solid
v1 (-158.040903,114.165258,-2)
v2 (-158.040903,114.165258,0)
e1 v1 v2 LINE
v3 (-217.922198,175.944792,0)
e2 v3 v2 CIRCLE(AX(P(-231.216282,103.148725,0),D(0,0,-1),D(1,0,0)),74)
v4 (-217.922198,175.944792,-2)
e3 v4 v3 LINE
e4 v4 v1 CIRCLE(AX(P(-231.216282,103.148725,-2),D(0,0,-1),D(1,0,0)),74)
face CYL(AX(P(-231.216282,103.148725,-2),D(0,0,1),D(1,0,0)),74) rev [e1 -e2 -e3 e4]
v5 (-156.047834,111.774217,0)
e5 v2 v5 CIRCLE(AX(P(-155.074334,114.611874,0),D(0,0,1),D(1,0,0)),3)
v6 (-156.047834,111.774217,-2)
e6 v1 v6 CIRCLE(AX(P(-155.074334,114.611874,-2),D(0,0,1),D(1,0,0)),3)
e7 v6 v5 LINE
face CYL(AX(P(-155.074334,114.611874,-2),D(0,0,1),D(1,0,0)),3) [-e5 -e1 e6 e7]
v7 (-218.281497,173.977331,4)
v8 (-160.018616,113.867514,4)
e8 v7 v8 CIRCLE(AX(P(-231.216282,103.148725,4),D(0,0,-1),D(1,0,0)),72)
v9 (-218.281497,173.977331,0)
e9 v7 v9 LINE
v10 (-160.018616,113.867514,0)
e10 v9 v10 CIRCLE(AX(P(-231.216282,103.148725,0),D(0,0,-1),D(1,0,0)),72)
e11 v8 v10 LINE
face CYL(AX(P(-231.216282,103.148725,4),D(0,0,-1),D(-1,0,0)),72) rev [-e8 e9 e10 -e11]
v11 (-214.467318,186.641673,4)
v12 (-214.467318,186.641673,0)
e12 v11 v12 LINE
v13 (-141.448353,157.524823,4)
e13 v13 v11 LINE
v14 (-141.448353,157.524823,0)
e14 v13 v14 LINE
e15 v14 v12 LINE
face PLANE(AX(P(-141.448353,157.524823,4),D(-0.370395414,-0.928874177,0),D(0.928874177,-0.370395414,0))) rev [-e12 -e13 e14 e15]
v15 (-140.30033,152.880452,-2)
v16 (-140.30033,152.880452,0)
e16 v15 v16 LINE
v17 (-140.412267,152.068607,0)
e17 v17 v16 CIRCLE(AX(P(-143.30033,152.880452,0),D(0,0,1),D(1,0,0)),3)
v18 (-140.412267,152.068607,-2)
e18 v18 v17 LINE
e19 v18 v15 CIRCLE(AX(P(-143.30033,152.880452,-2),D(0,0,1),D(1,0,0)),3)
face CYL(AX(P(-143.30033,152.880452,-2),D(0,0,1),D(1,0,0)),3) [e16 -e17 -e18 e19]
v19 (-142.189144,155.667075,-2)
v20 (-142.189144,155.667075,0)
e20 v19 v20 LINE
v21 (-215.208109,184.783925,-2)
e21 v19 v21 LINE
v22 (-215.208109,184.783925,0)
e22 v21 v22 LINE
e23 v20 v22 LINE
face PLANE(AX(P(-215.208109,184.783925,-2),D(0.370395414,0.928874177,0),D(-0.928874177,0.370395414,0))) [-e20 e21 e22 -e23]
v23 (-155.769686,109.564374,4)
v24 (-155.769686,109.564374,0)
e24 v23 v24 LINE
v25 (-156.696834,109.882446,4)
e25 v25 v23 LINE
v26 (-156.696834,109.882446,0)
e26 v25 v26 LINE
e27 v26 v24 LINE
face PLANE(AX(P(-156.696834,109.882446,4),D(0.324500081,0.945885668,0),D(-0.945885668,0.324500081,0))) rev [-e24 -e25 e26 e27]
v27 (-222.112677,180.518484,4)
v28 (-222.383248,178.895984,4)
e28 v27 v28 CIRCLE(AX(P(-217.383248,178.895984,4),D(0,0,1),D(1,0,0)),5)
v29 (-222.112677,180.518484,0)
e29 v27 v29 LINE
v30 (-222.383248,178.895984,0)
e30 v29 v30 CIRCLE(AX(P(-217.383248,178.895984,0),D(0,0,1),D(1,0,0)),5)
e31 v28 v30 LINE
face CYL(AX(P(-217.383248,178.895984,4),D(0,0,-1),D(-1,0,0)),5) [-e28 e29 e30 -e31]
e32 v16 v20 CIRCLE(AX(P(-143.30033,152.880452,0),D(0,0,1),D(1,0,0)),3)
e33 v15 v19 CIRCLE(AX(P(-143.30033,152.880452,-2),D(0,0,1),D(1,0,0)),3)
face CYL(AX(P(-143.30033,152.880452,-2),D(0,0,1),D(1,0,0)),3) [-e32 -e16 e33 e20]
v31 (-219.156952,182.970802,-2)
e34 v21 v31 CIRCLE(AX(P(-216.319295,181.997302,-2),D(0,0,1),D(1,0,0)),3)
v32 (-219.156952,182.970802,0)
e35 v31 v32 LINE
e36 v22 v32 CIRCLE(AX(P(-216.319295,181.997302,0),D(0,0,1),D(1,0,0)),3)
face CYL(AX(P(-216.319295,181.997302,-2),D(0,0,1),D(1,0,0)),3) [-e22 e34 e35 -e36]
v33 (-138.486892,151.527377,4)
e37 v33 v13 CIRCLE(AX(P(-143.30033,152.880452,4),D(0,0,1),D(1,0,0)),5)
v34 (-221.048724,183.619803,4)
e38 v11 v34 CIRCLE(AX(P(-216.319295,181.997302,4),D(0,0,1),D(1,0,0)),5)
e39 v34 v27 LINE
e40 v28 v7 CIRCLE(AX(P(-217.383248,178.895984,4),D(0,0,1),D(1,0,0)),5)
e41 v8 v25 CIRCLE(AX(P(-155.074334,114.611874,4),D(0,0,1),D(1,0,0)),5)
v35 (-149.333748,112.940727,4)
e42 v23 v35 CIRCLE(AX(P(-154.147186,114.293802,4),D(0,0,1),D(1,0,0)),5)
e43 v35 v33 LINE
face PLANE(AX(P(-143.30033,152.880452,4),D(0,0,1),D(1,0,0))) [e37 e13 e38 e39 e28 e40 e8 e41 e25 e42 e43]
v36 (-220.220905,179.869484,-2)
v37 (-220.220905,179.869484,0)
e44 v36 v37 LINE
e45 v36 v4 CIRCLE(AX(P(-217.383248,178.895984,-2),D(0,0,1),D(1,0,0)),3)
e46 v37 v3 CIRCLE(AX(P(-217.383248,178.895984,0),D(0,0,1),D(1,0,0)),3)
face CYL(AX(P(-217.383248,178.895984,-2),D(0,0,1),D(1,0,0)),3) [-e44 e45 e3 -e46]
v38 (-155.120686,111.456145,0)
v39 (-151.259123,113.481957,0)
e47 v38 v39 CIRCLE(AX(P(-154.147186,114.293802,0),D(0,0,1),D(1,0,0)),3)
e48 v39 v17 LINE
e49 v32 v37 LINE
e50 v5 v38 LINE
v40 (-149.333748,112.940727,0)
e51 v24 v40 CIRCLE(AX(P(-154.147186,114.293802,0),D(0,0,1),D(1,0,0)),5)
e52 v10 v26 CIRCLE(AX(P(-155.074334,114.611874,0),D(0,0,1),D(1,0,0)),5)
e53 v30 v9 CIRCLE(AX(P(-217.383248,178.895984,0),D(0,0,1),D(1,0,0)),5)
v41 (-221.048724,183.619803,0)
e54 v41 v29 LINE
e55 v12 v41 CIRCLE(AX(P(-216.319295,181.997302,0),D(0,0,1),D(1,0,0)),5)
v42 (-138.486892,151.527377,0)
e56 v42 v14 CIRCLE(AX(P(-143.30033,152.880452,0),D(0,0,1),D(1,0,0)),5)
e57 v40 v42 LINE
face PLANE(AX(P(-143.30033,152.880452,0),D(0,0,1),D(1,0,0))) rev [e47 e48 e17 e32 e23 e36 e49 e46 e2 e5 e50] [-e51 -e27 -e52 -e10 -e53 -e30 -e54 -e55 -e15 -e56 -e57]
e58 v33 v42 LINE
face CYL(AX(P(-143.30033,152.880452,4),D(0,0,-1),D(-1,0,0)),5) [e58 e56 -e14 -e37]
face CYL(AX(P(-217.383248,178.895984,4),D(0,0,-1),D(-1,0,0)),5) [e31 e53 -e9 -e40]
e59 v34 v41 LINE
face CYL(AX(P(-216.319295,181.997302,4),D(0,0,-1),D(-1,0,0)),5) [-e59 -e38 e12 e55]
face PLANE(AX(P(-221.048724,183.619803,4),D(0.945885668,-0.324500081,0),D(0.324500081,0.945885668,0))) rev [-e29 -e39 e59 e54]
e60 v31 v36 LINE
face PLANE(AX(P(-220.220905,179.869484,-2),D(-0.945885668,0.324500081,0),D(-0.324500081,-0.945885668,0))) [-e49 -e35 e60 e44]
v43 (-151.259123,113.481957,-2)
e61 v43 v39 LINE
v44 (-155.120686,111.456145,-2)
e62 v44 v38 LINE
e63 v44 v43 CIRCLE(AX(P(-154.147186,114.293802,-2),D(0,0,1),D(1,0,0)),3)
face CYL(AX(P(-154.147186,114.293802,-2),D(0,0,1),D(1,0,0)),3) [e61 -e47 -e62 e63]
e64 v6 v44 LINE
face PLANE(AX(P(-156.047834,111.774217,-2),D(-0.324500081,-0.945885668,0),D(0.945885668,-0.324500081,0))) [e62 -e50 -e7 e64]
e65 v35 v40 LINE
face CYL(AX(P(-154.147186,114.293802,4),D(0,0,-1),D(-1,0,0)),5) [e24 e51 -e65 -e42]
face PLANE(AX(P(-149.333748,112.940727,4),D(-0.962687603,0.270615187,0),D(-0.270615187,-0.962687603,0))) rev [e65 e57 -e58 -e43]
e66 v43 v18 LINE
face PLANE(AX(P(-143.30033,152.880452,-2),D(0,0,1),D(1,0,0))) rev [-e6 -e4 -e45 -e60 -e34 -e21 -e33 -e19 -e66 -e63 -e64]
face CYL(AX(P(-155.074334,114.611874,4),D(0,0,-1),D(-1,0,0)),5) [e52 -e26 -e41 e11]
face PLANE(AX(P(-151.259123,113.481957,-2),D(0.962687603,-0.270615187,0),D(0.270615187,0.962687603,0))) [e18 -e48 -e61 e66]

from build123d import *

# Parameters (mm, degrees)
EXTRUDE_1_DEPTH = 2
EXTRUDE_2_DEPTH = 4


with BuildPart() as part:
    # 草图1 → 凸台-拉伸1 (new body)
    with BuildSketch(Plane.XY):
        with BuildLine():
            Line((-151.259122885, 113.481956899), (-140.412267192, 152.068606889))
            ThreePointArc((-140.412267192, 152.068606889), (-140.610396656, 154.208706418), (-142.189143758, 155.667074982))
            Line((-142.189143758, 155.667074982), (-215.208108923, 184.78392473))
            ThreePointArc((-215.208108923, 184.78392473), (-217.571105228, 184.723649859), (-219.156952171, 182.97080244))
            Line((-219.156952171, 182.97080244), (-220.220905282, 179.86948426))
            ThreePointArc((-220.220905282, 179.86948426), (-219.971910037, 177.379794621), (-217.922197627, 175.944792124))
            ThreePointArc((-217.922197627, 175.944792124), (-178.080420962, 154.651932226), (-158.04090319, 114.165258148))
            ThreePointArc((-158.04090319, 114.165258148), (-157.378743964, 112.691016779), (-156.047834036, 111.774217336))
            Line((-156.047834036, 111.774217336), (-155.120685935, 111.456145455))
            ThreePointArc((-155.120685935, 111.456145455), (-152.753497975, 111.637181572), (-151.259122885, 113.481956899))
        make_face()
    extrude(amount=-EXTRUDE_1_DEPTH)

    # 草图2 → 凸台-拉伸2 (add)
    with BuildSketch(Plane.XY):
        with BuildLine():
            Line((-141.448352929, 157.524823337), (-214.467318094, 186.641673085))
            ThreePointArc((-214.467318094, 186.641673085), (-218.40564527, 186.541214966), (-221.048723508, 183.619802601))
            Line((-221.048723508, 183.619802601), (-222.112676618, 180.518484421))
            ThreePointArc((-222.112676618, 180.518484421), (-221.697684544, 176.369001689), (-218.281497194, 173.977330861))
            ThreePointArc((-218.281497194, 173.977330861), (-179.516525304, 153.259953663), (-160.01861612, 113.86751402))
            ThreePointArc((-160.01861612, 113.86751402), (-158.91501741, 111.410445071), (-156.696834197, 109.882445999))
            Line((-156.696834197, 109.882445999), (-155.769686096, 109.564374118))
            ThreePointArc((-155.769686096, 109.564374118), (-151.824372829, 109.86610098), (-149.33374768, 112.940726525))
            Line((-149.33374768, 112.940726525), (-138.486891987, 151.527376515))
            ThreePointArc((-138.486891987, 151.527376515), (-138.81710776, 155.094209064), (-141.448352929, 157.524823337))
        make_face()
    extrude(amount=EXTRUDE_2_DEPTH)


solid = part.part
